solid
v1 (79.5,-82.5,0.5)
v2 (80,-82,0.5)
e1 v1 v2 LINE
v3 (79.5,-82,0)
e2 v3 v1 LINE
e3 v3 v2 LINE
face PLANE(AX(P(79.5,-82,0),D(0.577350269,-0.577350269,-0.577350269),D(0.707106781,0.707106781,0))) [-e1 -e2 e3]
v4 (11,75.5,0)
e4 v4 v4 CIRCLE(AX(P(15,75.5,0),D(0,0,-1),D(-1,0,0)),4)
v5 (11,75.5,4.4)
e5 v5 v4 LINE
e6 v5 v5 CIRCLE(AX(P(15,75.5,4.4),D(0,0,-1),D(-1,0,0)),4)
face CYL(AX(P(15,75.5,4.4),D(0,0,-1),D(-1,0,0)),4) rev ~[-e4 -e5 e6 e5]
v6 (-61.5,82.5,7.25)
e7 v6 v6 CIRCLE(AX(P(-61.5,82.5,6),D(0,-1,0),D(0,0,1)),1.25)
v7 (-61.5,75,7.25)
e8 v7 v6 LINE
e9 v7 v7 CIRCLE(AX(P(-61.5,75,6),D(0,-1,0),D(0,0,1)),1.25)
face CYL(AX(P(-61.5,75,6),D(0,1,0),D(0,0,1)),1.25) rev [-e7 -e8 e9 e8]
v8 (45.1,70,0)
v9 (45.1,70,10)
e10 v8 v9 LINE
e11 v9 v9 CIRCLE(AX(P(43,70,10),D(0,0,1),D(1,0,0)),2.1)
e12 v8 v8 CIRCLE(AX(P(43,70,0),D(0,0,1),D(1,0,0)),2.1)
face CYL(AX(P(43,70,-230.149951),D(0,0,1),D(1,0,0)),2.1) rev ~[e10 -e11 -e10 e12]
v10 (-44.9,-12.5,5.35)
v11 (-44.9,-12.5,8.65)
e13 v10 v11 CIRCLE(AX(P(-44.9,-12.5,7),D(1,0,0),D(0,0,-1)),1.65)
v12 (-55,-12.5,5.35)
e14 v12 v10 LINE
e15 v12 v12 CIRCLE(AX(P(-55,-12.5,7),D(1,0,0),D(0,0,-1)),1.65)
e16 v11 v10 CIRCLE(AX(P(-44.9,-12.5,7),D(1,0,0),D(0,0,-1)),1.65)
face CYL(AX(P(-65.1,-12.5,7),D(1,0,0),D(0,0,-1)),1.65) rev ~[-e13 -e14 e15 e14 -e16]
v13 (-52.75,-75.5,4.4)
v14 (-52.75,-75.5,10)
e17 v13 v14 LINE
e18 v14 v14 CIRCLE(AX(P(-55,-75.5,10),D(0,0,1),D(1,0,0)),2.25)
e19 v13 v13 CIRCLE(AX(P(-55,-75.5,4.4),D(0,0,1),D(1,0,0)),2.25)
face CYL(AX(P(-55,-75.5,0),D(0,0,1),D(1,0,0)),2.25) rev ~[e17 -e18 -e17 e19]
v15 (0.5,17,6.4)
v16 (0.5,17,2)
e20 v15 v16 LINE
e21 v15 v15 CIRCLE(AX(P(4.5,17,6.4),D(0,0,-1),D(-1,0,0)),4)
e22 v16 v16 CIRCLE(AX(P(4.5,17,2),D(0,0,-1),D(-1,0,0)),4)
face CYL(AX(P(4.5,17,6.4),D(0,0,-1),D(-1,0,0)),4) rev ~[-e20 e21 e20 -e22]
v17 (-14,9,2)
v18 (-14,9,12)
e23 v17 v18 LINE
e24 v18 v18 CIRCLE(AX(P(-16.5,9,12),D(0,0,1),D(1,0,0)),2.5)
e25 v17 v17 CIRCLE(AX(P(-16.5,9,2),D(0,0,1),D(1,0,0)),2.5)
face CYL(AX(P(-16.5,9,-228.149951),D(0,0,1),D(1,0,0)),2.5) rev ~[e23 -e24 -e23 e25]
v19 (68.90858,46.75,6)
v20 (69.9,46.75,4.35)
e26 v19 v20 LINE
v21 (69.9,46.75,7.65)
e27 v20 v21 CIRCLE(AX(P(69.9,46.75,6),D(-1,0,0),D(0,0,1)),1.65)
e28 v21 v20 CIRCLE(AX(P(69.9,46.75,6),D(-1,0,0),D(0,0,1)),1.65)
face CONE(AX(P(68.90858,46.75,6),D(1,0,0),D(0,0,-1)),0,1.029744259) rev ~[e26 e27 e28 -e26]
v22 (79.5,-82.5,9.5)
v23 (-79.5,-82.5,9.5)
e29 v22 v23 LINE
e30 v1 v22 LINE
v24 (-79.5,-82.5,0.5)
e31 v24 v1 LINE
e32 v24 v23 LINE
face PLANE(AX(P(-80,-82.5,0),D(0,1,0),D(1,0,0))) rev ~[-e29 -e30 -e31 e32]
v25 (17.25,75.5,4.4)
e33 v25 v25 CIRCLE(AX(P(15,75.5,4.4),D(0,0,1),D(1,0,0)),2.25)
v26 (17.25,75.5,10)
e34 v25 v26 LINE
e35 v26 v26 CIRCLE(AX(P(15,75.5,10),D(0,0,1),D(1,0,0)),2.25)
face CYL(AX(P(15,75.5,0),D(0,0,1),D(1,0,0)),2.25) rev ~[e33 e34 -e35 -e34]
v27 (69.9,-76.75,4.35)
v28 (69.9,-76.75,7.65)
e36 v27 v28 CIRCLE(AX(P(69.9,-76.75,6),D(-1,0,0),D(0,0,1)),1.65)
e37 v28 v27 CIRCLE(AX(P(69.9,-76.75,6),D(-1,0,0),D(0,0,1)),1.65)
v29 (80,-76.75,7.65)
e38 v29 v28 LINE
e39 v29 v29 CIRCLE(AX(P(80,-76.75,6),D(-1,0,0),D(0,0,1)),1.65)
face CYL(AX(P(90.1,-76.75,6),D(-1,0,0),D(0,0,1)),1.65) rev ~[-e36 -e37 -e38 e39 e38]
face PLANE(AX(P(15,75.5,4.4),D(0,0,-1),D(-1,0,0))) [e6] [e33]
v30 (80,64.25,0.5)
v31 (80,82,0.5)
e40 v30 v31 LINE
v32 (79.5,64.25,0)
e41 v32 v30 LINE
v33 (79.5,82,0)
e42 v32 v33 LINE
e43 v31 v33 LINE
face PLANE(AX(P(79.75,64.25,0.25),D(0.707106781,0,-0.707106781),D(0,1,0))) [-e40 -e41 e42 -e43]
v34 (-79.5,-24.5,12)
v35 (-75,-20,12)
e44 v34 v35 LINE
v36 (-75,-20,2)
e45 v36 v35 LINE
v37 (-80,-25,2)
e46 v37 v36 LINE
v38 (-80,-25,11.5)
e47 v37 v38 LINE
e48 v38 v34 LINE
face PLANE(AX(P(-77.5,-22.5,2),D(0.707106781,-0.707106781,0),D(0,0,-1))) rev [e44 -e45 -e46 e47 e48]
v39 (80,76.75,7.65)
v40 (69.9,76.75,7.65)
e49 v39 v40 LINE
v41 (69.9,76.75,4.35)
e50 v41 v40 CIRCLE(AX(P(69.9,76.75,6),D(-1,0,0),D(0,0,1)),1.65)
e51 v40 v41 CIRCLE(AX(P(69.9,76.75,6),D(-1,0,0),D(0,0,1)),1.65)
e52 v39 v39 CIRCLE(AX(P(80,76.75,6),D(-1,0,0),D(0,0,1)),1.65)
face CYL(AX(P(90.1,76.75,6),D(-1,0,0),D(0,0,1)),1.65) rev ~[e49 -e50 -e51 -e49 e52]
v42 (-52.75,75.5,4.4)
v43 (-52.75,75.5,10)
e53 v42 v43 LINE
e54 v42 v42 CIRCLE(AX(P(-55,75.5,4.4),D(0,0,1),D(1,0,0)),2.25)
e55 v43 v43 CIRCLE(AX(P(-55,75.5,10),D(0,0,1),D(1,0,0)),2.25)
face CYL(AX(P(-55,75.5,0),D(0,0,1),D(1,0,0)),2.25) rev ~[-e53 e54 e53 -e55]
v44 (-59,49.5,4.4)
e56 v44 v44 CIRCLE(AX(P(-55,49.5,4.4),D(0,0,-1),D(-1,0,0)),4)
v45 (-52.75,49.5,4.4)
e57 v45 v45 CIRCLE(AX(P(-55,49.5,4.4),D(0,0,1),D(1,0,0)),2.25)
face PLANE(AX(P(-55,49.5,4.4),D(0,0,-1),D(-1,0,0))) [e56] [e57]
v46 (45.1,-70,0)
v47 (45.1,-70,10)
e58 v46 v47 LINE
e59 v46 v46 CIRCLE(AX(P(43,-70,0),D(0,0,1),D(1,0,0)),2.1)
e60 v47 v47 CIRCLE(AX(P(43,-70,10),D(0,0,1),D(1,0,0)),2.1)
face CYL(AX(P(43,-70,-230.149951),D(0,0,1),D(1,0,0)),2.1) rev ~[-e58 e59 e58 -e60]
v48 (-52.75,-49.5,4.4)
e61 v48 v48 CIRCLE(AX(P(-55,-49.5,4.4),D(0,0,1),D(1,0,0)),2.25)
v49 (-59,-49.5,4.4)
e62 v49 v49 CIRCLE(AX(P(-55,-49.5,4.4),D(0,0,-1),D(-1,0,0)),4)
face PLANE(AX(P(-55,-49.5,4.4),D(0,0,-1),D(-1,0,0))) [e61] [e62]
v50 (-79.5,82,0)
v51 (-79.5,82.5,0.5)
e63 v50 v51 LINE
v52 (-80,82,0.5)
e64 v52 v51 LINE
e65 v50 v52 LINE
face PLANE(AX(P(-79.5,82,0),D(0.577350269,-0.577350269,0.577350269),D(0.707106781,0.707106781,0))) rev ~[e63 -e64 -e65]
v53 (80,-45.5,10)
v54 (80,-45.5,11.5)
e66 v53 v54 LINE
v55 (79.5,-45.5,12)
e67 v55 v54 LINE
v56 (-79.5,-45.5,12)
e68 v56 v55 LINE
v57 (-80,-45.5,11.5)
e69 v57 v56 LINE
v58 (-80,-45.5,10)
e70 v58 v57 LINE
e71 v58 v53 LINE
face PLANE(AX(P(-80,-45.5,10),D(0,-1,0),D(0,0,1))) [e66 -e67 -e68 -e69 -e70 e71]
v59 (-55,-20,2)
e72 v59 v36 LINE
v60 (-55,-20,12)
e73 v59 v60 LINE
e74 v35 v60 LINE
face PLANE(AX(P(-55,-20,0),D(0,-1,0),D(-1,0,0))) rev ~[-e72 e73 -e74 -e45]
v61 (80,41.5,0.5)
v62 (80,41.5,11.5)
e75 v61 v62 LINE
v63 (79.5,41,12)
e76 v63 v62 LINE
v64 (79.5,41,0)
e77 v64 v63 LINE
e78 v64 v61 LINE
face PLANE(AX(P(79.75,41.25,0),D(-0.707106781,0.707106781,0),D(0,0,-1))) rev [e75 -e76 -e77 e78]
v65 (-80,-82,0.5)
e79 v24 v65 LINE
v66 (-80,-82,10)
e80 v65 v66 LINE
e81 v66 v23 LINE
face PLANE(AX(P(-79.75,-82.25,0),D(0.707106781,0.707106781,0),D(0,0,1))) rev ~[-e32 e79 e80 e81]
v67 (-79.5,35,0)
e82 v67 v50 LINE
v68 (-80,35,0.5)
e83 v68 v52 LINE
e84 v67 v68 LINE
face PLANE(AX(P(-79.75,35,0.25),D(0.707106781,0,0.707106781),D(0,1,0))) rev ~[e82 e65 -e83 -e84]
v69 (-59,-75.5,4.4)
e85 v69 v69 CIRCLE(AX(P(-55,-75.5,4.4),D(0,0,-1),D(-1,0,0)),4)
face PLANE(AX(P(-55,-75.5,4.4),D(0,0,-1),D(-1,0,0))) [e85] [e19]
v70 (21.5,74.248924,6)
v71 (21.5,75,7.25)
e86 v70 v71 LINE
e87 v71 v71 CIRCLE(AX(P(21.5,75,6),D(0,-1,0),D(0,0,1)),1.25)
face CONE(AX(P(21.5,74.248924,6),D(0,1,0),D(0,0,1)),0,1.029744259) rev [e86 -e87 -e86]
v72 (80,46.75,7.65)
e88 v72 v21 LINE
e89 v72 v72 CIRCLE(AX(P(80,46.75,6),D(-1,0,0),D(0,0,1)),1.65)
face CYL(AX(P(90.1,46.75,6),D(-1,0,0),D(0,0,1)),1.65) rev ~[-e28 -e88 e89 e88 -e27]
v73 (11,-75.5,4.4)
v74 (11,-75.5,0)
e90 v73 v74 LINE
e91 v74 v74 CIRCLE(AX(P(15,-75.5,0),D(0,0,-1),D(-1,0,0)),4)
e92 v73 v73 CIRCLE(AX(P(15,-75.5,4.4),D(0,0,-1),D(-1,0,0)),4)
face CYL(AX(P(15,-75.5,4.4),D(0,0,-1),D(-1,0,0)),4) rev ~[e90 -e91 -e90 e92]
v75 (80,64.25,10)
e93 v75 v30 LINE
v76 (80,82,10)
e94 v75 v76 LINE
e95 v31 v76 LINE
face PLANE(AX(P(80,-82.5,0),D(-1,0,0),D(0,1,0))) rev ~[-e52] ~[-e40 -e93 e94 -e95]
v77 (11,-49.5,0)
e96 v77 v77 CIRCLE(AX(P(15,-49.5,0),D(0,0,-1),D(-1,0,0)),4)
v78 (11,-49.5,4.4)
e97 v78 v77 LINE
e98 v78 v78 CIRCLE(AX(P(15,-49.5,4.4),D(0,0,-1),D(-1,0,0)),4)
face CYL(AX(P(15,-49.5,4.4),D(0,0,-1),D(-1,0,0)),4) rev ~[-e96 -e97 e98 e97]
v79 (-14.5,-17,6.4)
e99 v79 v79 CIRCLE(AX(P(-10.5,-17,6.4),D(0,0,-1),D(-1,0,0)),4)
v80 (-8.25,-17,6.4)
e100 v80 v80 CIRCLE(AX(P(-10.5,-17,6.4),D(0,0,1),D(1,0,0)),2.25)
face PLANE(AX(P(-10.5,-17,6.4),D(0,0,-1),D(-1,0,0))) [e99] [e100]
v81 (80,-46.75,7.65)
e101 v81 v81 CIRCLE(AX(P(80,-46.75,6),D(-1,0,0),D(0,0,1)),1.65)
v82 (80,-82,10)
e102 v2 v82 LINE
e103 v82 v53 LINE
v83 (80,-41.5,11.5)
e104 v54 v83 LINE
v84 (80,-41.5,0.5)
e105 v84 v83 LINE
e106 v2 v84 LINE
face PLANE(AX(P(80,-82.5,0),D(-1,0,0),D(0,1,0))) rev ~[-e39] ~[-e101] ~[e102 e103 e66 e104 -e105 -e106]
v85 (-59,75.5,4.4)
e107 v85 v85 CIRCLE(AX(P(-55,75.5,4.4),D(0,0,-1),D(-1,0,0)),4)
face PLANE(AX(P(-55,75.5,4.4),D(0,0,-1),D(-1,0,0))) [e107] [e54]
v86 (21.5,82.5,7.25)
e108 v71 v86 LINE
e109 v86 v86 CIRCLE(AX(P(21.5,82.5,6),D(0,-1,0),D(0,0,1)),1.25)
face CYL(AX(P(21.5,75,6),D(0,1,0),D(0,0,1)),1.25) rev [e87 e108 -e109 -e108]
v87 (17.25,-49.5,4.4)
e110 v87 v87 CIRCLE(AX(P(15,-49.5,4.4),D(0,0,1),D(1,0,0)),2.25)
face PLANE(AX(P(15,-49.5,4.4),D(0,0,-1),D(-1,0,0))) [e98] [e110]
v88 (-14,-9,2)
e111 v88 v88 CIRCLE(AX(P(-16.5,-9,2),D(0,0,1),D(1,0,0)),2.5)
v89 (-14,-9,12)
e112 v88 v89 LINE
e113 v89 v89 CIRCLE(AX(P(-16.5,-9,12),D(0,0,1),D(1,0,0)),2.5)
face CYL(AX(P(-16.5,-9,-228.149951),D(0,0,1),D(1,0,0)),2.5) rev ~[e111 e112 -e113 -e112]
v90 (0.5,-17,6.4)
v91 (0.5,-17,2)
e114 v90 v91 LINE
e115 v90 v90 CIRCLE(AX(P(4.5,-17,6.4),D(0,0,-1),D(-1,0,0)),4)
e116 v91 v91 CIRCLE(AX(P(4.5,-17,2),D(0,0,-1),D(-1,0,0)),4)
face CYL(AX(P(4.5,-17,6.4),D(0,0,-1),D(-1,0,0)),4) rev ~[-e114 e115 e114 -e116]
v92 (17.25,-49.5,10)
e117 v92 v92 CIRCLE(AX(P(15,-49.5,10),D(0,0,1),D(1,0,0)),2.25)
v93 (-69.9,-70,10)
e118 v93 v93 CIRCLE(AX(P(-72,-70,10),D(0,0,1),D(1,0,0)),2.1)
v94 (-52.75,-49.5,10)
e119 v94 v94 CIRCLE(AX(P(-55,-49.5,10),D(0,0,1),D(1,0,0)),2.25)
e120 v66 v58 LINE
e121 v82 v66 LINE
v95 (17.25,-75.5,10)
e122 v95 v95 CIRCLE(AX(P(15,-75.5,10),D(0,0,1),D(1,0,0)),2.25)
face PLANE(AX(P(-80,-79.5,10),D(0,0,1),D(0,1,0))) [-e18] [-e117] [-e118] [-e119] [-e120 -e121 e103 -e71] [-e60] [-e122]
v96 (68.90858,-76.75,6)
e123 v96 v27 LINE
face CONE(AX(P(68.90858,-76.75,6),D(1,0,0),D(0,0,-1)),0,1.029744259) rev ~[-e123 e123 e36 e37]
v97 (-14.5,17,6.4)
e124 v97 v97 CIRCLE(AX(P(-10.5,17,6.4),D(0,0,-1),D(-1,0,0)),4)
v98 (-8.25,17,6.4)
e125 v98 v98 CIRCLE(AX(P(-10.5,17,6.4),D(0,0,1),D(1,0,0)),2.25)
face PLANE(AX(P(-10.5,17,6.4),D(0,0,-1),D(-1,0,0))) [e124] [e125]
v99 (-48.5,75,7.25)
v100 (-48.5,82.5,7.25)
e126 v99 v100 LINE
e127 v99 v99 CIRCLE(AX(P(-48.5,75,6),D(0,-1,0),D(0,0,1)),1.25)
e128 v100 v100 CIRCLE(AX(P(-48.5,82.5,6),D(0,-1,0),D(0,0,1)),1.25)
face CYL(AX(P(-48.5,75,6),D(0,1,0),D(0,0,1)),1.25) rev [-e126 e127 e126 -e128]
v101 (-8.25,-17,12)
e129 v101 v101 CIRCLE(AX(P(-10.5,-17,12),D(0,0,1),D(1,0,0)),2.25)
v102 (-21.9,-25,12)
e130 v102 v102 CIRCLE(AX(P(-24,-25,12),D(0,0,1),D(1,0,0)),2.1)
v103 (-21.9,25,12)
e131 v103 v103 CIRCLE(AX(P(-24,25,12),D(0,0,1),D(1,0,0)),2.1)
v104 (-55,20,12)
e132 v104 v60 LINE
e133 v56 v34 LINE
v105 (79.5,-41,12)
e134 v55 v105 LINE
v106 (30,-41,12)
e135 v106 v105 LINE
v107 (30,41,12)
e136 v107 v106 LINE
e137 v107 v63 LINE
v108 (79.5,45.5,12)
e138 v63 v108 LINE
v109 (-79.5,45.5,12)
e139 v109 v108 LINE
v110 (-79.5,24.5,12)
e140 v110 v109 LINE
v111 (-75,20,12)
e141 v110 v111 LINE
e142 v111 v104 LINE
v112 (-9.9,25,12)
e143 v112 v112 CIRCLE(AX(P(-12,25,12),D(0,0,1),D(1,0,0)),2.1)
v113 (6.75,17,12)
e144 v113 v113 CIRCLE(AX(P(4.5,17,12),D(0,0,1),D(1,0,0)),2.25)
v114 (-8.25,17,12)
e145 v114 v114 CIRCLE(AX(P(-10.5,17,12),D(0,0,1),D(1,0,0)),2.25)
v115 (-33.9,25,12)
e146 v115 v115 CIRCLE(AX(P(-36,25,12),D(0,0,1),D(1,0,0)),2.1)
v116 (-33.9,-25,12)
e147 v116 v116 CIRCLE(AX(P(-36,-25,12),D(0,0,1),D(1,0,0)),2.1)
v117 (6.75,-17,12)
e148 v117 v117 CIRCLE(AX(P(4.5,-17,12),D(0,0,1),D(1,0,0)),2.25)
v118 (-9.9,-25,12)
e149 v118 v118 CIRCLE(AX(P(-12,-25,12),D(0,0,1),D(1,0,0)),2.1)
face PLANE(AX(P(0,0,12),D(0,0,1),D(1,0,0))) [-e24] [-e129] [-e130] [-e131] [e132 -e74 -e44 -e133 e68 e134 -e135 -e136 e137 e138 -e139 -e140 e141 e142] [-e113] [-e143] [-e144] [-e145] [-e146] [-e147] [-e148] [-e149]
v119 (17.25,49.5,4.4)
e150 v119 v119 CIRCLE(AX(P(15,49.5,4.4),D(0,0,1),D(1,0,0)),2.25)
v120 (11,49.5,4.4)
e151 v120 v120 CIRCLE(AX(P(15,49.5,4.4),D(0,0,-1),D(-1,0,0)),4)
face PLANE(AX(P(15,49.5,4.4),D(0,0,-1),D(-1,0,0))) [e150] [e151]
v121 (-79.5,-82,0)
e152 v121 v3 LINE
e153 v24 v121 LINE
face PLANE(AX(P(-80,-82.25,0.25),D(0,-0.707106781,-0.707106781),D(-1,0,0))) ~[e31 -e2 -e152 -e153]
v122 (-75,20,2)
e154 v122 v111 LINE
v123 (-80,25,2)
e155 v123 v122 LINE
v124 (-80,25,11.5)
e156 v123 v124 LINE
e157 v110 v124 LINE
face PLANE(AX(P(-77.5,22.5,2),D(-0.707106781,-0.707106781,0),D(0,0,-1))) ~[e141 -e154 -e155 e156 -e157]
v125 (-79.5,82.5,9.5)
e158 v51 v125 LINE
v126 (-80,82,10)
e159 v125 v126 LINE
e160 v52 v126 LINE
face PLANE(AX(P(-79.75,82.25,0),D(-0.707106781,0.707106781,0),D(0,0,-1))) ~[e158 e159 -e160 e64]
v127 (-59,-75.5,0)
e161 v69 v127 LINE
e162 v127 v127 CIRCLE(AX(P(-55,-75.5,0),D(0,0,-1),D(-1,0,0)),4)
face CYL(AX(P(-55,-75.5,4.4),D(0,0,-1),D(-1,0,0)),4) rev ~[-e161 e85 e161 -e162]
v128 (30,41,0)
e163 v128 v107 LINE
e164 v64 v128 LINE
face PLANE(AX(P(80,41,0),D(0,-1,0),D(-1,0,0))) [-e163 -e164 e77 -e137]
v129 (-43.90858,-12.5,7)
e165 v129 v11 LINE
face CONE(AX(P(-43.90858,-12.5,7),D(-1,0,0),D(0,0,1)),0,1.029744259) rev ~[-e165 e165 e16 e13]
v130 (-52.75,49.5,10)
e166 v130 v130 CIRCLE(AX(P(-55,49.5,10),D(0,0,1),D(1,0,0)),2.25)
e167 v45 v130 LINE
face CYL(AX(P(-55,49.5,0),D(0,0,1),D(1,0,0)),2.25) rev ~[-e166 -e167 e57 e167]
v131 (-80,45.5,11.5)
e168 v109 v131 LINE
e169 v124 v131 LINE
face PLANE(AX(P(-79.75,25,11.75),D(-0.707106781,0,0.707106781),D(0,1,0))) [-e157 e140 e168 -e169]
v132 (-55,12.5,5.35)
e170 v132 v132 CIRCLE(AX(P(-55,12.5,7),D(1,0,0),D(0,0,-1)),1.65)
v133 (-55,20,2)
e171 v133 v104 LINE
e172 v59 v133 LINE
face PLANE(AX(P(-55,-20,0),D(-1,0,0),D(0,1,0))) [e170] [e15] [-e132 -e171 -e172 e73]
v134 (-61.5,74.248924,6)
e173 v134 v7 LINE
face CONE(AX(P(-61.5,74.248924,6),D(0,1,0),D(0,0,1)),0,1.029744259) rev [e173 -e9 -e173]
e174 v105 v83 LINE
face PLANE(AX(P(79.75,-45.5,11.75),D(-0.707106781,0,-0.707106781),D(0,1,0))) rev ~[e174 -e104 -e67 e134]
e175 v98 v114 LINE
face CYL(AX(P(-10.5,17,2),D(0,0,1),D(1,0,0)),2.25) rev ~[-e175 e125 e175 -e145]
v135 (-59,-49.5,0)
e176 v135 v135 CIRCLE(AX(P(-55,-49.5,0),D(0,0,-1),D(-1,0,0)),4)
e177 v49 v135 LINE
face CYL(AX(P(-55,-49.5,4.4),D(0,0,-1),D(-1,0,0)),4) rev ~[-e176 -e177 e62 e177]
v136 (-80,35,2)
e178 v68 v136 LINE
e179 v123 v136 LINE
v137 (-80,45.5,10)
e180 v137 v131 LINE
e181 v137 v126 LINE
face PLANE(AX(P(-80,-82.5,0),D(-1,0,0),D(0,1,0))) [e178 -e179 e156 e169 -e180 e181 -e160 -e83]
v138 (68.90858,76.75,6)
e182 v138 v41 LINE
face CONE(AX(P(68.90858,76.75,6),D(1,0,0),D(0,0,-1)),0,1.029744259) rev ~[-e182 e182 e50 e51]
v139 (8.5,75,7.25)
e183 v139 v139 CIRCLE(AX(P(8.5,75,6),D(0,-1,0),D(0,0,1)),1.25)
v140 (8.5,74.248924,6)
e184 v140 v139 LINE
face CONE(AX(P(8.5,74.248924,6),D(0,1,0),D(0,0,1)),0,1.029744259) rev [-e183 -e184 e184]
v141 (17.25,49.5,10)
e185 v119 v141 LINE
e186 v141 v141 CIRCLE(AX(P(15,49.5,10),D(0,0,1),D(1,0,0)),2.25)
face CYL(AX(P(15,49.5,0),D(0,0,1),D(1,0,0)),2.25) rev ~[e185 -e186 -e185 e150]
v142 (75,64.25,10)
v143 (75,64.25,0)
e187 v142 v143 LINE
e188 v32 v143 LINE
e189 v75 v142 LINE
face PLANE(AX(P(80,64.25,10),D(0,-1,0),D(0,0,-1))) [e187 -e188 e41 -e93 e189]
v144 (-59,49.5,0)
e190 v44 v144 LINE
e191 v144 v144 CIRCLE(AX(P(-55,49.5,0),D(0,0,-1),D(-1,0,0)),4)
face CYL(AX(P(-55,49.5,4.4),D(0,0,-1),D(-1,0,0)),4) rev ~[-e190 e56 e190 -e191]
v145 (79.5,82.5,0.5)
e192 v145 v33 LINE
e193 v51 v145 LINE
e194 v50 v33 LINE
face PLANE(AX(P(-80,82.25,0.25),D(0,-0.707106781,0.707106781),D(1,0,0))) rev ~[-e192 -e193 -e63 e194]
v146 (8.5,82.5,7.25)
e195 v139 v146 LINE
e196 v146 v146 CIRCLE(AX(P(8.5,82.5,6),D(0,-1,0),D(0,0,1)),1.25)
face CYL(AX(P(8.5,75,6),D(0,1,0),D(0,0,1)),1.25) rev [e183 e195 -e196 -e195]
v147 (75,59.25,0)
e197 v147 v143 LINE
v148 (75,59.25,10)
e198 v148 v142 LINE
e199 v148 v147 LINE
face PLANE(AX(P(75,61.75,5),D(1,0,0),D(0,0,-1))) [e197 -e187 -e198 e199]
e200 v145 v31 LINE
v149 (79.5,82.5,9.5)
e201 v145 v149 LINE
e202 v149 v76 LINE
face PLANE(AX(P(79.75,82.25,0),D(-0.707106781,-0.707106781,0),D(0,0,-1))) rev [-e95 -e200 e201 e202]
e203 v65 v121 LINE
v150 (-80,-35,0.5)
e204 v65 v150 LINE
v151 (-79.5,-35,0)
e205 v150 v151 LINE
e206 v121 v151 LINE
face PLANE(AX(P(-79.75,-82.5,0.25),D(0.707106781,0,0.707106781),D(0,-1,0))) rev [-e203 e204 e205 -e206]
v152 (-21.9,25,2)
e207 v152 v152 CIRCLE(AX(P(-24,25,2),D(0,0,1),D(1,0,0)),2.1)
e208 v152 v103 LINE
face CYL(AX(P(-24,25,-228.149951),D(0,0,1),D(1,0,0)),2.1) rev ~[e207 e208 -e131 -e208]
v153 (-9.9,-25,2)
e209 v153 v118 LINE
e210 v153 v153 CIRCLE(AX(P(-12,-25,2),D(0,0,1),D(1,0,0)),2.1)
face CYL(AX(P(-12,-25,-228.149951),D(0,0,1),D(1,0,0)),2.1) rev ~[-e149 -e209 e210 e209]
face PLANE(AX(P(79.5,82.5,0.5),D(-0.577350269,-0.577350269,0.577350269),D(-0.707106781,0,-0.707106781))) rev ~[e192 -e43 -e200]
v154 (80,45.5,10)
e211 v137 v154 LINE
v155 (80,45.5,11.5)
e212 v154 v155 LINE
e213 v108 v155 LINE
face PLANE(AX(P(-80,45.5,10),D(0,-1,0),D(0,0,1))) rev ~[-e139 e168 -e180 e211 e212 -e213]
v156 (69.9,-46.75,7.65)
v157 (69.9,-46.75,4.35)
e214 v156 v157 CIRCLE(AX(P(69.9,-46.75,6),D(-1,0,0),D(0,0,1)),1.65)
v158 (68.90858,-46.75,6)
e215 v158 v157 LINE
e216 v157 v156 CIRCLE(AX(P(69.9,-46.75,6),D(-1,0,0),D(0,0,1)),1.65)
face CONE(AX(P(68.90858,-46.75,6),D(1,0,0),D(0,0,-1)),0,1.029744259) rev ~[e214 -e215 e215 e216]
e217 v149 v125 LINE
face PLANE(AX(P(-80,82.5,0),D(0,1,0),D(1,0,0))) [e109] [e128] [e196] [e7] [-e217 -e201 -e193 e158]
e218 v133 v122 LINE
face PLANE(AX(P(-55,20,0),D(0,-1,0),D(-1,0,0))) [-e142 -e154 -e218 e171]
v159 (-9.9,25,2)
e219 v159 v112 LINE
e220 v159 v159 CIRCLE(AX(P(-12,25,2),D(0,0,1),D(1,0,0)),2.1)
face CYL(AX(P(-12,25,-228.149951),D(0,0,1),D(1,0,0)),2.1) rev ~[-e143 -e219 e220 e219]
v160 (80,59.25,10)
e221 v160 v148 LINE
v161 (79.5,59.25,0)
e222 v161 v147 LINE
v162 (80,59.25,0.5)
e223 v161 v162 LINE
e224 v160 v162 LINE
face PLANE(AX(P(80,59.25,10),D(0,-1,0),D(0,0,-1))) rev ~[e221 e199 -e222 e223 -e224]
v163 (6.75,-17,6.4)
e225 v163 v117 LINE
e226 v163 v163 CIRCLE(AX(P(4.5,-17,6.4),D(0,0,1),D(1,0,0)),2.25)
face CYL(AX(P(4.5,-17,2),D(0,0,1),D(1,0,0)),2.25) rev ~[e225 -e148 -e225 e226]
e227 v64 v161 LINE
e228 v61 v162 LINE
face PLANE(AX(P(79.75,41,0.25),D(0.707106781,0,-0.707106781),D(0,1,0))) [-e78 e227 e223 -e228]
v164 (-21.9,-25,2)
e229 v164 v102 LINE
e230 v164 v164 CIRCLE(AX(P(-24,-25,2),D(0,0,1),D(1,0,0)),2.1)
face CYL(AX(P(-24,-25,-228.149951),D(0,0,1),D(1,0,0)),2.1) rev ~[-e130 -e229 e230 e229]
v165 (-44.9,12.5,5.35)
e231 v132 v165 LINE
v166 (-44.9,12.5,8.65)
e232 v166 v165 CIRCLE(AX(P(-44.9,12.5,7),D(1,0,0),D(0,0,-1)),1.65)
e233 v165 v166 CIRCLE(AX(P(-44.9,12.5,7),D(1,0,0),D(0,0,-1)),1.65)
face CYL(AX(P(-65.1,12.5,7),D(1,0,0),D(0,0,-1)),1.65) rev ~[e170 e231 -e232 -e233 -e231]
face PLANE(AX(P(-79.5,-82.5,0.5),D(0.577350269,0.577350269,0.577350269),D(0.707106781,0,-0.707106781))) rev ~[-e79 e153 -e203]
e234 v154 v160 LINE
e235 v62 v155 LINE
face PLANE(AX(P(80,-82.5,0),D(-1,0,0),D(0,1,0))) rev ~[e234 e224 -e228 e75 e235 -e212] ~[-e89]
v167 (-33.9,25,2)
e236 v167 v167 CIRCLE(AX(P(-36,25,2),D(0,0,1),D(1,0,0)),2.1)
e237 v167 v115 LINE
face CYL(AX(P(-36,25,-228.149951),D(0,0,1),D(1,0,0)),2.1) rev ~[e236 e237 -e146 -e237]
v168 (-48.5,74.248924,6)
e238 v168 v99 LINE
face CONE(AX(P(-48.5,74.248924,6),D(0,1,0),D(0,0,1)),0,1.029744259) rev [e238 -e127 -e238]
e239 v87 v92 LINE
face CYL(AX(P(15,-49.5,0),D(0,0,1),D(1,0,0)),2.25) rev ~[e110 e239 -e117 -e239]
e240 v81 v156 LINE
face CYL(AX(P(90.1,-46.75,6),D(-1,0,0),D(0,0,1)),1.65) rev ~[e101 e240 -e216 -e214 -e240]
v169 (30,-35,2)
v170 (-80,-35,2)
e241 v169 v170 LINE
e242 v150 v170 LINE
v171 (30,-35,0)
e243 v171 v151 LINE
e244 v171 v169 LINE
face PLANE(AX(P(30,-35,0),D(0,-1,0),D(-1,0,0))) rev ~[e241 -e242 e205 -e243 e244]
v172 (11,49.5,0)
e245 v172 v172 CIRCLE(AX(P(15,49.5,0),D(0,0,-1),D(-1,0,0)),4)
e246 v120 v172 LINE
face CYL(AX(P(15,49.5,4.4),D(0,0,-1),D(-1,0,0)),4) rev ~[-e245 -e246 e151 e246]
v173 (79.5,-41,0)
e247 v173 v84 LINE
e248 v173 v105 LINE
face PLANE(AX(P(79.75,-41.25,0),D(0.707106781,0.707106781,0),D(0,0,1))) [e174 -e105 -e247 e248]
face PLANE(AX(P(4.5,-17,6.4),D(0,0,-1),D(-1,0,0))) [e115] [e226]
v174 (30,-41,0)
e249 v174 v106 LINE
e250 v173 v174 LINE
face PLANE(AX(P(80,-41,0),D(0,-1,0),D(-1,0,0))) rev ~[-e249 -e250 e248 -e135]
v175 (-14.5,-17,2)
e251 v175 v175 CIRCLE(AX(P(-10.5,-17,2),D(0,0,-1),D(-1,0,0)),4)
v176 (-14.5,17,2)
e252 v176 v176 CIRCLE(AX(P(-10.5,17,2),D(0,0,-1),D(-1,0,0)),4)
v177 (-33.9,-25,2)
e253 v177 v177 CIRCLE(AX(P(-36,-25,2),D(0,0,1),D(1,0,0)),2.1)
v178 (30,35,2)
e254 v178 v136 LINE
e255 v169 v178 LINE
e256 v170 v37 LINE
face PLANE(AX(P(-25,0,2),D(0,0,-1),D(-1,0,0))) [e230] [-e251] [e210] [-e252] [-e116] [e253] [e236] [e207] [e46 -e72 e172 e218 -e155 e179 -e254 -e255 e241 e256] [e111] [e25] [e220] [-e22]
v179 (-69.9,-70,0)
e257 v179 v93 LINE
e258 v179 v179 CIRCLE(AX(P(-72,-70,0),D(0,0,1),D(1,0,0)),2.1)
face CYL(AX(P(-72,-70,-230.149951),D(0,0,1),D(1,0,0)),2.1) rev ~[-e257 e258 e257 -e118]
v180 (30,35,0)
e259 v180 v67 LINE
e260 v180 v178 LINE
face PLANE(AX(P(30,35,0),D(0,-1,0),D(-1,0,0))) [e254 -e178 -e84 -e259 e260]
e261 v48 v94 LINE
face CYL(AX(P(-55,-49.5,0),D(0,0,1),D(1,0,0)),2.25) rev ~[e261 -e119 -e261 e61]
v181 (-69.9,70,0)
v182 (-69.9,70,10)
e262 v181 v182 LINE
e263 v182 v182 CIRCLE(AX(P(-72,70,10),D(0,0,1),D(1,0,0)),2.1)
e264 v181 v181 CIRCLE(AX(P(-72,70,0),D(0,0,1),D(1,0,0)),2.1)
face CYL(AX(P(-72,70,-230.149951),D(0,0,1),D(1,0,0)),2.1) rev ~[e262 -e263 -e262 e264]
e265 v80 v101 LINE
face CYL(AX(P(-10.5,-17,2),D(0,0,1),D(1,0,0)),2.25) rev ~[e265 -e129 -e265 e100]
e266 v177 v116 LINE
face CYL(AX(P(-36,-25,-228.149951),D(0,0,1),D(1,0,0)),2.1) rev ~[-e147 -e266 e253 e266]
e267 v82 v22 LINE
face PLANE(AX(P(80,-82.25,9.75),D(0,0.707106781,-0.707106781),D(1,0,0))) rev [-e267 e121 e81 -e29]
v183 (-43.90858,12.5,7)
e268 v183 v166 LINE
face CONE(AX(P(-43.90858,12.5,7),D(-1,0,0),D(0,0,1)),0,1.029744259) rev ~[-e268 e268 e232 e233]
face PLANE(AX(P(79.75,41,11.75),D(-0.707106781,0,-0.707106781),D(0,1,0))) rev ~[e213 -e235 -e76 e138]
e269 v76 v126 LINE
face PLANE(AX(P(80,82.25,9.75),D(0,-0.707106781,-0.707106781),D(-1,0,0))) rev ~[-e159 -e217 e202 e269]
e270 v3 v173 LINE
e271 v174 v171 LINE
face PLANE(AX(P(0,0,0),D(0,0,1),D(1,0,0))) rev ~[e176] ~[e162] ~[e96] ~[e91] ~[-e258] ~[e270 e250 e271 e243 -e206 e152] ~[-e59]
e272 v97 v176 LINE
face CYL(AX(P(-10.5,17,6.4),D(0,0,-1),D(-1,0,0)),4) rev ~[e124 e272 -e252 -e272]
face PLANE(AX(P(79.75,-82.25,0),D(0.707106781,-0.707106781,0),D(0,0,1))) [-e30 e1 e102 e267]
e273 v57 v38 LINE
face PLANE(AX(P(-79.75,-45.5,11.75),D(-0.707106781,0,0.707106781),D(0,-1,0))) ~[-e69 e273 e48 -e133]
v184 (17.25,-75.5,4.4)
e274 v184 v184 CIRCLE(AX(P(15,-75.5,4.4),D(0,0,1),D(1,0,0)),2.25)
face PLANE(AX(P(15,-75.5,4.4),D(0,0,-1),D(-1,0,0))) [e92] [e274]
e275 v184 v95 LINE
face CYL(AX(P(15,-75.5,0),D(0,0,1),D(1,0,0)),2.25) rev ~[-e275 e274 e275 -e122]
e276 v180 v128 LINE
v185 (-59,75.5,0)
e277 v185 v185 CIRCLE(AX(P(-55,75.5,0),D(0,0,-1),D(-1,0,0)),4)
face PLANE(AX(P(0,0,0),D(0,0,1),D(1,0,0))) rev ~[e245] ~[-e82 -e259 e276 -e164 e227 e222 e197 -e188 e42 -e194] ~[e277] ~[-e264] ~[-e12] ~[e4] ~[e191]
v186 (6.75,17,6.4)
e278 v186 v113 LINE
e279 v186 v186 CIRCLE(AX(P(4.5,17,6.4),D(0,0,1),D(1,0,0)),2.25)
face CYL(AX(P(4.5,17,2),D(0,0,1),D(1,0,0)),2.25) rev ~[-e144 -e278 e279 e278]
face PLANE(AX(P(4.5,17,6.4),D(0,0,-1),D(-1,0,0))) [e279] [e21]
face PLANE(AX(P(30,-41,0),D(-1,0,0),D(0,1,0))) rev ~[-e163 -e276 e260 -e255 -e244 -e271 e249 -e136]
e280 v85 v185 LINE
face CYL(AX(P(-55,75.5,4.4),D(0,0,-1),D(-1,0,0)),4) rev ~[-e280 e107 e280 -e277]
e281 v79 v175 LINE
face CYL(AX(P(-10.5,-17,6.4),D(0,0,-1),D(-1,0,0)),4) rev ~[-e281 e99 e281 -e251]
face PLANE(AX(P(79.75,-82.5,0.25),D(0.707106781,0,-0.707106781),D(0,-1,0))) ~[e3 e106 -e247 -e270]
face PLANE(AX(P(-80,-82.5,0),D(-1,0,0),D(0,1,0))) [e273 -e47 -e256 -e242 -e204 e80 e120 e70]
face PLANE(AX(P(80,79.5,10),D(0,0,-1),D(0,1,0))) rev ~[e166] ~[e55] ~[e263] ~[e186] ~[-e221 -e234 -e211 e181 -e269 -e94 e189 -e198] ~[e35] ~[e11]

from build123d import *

# Parameters (mm, degrees)
SKETCH_1_W                   = 160
SKETCH_1_H                   = 165
EXTRUDE_1_DEPTH              = 12
SKETCH_2_W                   = 50
SKETCH_2_H                   = 82
CUT_EXTRUDE_1_DEPTH          = 116.543281934
SKETCH_3_W                   = 2
SKETCH_3_H                   = 34
CUT_EXTRUDE_2_DEPTH          = 181.416878368
HOLE_WIZARD_M4_2_D           = 4.5
HOLE_WIZARD_M4_2_CBORE_D     = 8
HOLE_WIZARD_M4_2_CBORE_DEPTH = 4.4
SKETCH_6_W                   = 110
SKETCH_6_H                   = 70
CUT_EXTRUDE_3_DEPTH          = 2
HOLE_WIZARD_M4_1_D           = 4.5
HOLE_WIZARD_M4_1_CBORE_D     = 8
HOLE_WIZARD_M4_1_CBORE_DEPTH = 4.4
MM_2_D                       = 5
HOLE_WIZARD_M5_1_D           = 4.2
HOLE_WIZARD_M4_1_2_D         = 3.3
HOLE_WIZARD_M4_1_2_DEPTH     = 10.1
HOLE_WIZARD_M4_1_2_TIP       = 0.991420021
SKETCH_17_W                  = 10
SKETCH_17_H                  = 5
CUT_EXTRUDE_4_DEPTH          = 5
HOLE_WIZARD_M5_2_D           = 4.2
PATTERN_LINEAR_1_COUNT       = 3
PATTERN_LINEAR_1_PITCH       = 12
SKETCH_20_W                  = 25
SKETCH_20_H                  = 40
CUT_EXTRUDE_5_DEPTH          = 116.543281934
CHAMFER_1_SIZE               = 5
HOLE_WIZARD_M4_2_2_D         = 3.3
HOLE_WIZARD_M4_2_2_DEPTH     = 10.1
HOLE_WIZARD_M4_2_2_TIP       = 0.991420021
HOLE_WIZARD_M3_1_AT_2_COUNT  = 2
HOLE_WIZARD_M3_1_AT_2_PITCH  = 13
PATTERN_LINEAR_2_COUNT       = 2
PATTERN_LINEAR_2_PITCH       = 70
SKETCH_25_W                  = 2
SKETCH_25_H                  = 3
CUT_EXTRUDE_6_DEPTH          = 181.416878368
CHAMFER_2_SIZE               = 0.5


with BuildPart() as part:
    # 草图1 → 凸台-拉伸1 (new body)
    with BuildSketch(Plane.XY):
        Rectangle(SKETCH_1_W, SKETCH_1_H)
    extrude(amount=EXTRUDE_1_DEPTH)

    # 草图2 → 切除-拉伸1 (cut, through all)
    with BuildSketch(Plane(origin=(0, 0, 0), x_dir=(-1, 0, 0), z_dir=(0, 0, -1))):
        with Locations((-55, 0)):
            Rectangle(SKETCH_2_W, SKETCH_2_H)
    extrude(amount=-CUT_EXTRUDE_1_DEPTH, mode=Mode.SUBTRACT)

    # 草图3 → 切除-拉伸2 (cut, through all)
    with BuildSketch(Plane.ZY.offset(80)):
        with Locations((11, 62.5)):
            Rectangle(SKETCH_3_W, SKETCH_3_H)
        with Locations((11, -62.5)):
            Rectangle(SKETCH_3_W, SKETCH_3_H)
    extrude(amount=-CUT_EXTRUDE_2_DEPTH, mode=Mode.SUBTRACT)

    # Hole Wizard M4 _2 (through all)
    with Locations(Plane(origin=(0, 0, 0), x_dir=(-1, 0, 0), z_dir=(0, 0, -1))):
        with Locations((-15, 49.5), (-15, 75.5), (-15, -75.5), (-15, -49.5), (55, -75.5), (55, -49.5), (55, 49.5), (55, 75.5)):
            CounterBoreHole(HOLE_WIZARD_M4_2_D / 2, HOLE_WIZARD_M4_2_CBORE_D / 2, HOLE_WIZARD_M4_2_CBORE_DEPTH)

    # 草图6 → 切除-拉伸3 (cut)
    with BuildSketch(Plane(origin=(0, 0, 0), x_dir=(-1, 0, 0), z_dir=(0, 0, -1))):
        with Locations((25, 0)):
            Rectangle(SKETCH_6_W, SKETCH_6_H)
    extrude(amount=-CUT_EXTRUDE_3_DEPTH, mode=Mode.SUBTRACT)

    # Hole Wizard M4 _1 (through all)
    with Locations(Plane(origin=(0, 0, 2), x_dir=(-1, 0, 0), z_dir=(0, 0, -1))):
        with Locations((-4.5, -17), (-4.5, 17), (10.5, -17), (10.5, 17)):
            CounterBoreHole(HOLE_WIZARD_M4_1_D / 2, HOLE_WIZARD_M4_1_CBORE_D / 2, HOLE_WIZARD_M4_1_CBORE_DEPTH)

    # 大小mm 暗销孔2 (through all)
    with Locations(Plane(origin=(0, 0, 2), x_dir=(-1, 0, 0), z_dir=(0, 0, -1))):
        with Locations((16.5, -9), (16.5, 9)):
            Hole(MM_2_D / 2)

    # M5 螺纹孔1 (through all)
    with Locations(Plane(origin=(0, 0, 0), x_dir=(-1, 0, 0), z_dir=(0, 0, -1))):
        with Locations((72, 70), (-43, 70), (-43, -70), (72, -70)):
            Hole(HOLE_WIZARD_M5_1_D / 2)

    # Hole Wizard M4 _1 2
    with Locations(Plane(origin=(80, 0, 0), x_dir=(0, 0, -1), z_dir=(1, 0, 0))):
        with Locations((-6, 76.75), (-6, 46.75), (-6, -46.75), (-6, -76.75)):
            Hole(HOLE_WIZARD_M4_1_2_D / 2, depth=HOLE_WIZARD_M4_1_2_DEPTH)
            with Locations((0, 0, -(HOLE_WIZARD_M4_1_2_DEPTH + HOLE_WIZARD_M4_1_2_TIP / 2))):  # 118° drill point
                Cone(0, HOLE_WIZARD_M4_1_2_D / 2, HOLE_WIZARD_M4_1_2_TIP, mode=Mode.SUBTRACT)

    # 草图17 → 切除-拉伸4 (cut)
    with BuildSketch(Plane(origin=(80, 0, 0), x_dir=(0, 0, -1), z_dir=(1, 0, 0))):
        with Locations((-5, 61.75)):
            Rectangle(SKETCH_17_W, SKETCH_17_H)
    extrude(amount=-CUT_EXTRUDE_4_DEPTH, mode=Mode.SUBTRACT)

    # M5 螺纹孔2 (through all)
    with Locations(Plane(origin=(0, 0, 2), x_dir=(-1, 0, 0), z_dir=(0, 0, -1))):
        with Locations((12, 25), (12, -25)):
            hole_wizard_m5_2 = Hole(HOLE_WIZARD_M5_2_D / 2)

    # 阵列(线性)1: M5 螺纹孔2 ×3
    with Locations(*[(-i * PATTERN_LINEAR_1_PITCH, 0, 0) for i in range(1, PATTERN_LINEAR_1_COUNT)]):
        add(hole_wizard_m5_2, mode=Mode.SUBTRACT)

    # 草图20 → 切除-拉伸5 (cut, through all)
    with BuildSketch(Plane(origin=(0, 0, 0), x_dir=(-1, 0, 0), z_dir=(0, 0, -1))):
        with Locations((67.5, 0)):
            Rectangle(SKETCH_20_W, SKETCH_20_H)
    extrude(amount=-CUT_EXTRUDE_5_DEPTH, mode=Mode.SUBTRACT)

    # 倒角1
    chamfer_1_edges = [part.edges().sort_by_distance(p)[0] for p in [
        (-80, 20, 7),
        (-80, -20, 7),
    ]]
    chamfer(chamfer_1_edges, length=CHAMFER_1_SIZE)

    # Hole Wizard M4 _2 2
    with Locations(Plane.ZY.offset(55)):
        with Locations((7, 12.5), (7, -12.5)):
            Hole(HOLE_WIZARD_M4_2_2_D / 2, depth=HOLE_WIZARD_M4_2_2_DEPTH)
            with Locations((0, 0, -(HOLE_WIZARD_M4_2_2_DEPTH + HOLE_WIZARD_M4_2_2_TIP / 2))):  # 118° drill point
                Cone(0, HOLE_WIZARD_M4_2_2_D / 2, HOLE_WIZARD_M4_2_2_TIP, mode=Mode.SUBTRACT)

    # 草图24 → M3 螺纹孔1 (revolve, cut)
    with BuildSketch(Plane(origin=(-61.5, 82.5, 6), x_dir=(0, 0, 1), z_dir=(1, 0, 0))):
        Polygon((0, 0), (0, 8.251075774), (1.25, 7.5), (1.25, 0), align=None)
    hole_wizard_m3_1 = revolve(axis=Axis((-61.5, 88.85, 6), (0, -1, 0)), mode=Mode.SUBTRACT)

    # M3 螺纹孔1 at 2: M3 螺纹孔1 ×2
    with Locations(*[(i * HOLE_WIZARD_M3_1_AT_2_PITCH, 0, 0) for i in range(1, HOLE_WIZARD_M3_1_AT_2_COUNT)]):
        add(hole_wizard_m3_1, mode=Mode.SUBTRACT)

    # 阵列(线性)2: M3 螺纹孔1 ×2
    with Locations(*[(i * PATTERN_LINEAR_2_PITCH, 0, 0) for i in range(1, PATTERN_LINEAR_2_COUNT)]):
        add(hole_wizard_m3_1, mode=Mode.SUBTRACT)

    # 阵列(线性)2 copy 1 sketch → 阵列(线性)2 copy 1 (revolve, cut)
    with BuildSketch(Plane(origin=(21.5, 82.5, 6), x_dir=(0, 0, 1), z_dir=(1, 0, 0))):
        Polygon((0, 0), (0, 8.251075774), (1.25, 7.5), (1.25, 0), align=None)
    revolve(axis=Axis((21.5, 88.85, 6), (0, -1, 0)), mode=Mode.SUBTRACT)

    # 草图25 → 切除-拉伸6 (cut, through all)
    with BuildSketch(Plane(origin=(80, 0, 0), x_dir=(0, 0, -1), z_dir=(1, 0, 0))):
        with Locations((-11, 81)):
            Rectangle(SKETCH_25_W, SKETCH_25_H)
        with Locations((-11, -81)):
            Rectangle(SKETCH_25_W, SKETCH_25_H)
    extrude(amount=-CUT_EXTRUDE_6_DEPTH, mode=Mode.SUBTRACT)

    # 倒角2
    chamfer_2_edges = [part.edges().sort_by_distance(p)[0] for p in [
        (-80, -58.75, 0),
        (80, 50.125, 0),
        (80, 43.25, 12),
        (80, -41, 6),
        (80, 41, 6),
        (80, 73.375, 0),
        (-80, -35.25, 12),
        (-80, 35.25, 12),
        (80, -43.25, 12),
        (80, -82.5, 5),
        (-80, -82.5, 5),
        (-80, 82.5, 5),
        (80, 82.5, 5),
        (0, 82.5, 10),
        (0, -82.5, 10),
        (0, -82.5, 0),
        (-80, 58.75, 0),
        (0, 82.5, 0),
        (80, -61.75, 0),
    ]]
    chamfer(chamfer_2_edges, length=CHAMFER_2_SIZE)


solid = part.part
